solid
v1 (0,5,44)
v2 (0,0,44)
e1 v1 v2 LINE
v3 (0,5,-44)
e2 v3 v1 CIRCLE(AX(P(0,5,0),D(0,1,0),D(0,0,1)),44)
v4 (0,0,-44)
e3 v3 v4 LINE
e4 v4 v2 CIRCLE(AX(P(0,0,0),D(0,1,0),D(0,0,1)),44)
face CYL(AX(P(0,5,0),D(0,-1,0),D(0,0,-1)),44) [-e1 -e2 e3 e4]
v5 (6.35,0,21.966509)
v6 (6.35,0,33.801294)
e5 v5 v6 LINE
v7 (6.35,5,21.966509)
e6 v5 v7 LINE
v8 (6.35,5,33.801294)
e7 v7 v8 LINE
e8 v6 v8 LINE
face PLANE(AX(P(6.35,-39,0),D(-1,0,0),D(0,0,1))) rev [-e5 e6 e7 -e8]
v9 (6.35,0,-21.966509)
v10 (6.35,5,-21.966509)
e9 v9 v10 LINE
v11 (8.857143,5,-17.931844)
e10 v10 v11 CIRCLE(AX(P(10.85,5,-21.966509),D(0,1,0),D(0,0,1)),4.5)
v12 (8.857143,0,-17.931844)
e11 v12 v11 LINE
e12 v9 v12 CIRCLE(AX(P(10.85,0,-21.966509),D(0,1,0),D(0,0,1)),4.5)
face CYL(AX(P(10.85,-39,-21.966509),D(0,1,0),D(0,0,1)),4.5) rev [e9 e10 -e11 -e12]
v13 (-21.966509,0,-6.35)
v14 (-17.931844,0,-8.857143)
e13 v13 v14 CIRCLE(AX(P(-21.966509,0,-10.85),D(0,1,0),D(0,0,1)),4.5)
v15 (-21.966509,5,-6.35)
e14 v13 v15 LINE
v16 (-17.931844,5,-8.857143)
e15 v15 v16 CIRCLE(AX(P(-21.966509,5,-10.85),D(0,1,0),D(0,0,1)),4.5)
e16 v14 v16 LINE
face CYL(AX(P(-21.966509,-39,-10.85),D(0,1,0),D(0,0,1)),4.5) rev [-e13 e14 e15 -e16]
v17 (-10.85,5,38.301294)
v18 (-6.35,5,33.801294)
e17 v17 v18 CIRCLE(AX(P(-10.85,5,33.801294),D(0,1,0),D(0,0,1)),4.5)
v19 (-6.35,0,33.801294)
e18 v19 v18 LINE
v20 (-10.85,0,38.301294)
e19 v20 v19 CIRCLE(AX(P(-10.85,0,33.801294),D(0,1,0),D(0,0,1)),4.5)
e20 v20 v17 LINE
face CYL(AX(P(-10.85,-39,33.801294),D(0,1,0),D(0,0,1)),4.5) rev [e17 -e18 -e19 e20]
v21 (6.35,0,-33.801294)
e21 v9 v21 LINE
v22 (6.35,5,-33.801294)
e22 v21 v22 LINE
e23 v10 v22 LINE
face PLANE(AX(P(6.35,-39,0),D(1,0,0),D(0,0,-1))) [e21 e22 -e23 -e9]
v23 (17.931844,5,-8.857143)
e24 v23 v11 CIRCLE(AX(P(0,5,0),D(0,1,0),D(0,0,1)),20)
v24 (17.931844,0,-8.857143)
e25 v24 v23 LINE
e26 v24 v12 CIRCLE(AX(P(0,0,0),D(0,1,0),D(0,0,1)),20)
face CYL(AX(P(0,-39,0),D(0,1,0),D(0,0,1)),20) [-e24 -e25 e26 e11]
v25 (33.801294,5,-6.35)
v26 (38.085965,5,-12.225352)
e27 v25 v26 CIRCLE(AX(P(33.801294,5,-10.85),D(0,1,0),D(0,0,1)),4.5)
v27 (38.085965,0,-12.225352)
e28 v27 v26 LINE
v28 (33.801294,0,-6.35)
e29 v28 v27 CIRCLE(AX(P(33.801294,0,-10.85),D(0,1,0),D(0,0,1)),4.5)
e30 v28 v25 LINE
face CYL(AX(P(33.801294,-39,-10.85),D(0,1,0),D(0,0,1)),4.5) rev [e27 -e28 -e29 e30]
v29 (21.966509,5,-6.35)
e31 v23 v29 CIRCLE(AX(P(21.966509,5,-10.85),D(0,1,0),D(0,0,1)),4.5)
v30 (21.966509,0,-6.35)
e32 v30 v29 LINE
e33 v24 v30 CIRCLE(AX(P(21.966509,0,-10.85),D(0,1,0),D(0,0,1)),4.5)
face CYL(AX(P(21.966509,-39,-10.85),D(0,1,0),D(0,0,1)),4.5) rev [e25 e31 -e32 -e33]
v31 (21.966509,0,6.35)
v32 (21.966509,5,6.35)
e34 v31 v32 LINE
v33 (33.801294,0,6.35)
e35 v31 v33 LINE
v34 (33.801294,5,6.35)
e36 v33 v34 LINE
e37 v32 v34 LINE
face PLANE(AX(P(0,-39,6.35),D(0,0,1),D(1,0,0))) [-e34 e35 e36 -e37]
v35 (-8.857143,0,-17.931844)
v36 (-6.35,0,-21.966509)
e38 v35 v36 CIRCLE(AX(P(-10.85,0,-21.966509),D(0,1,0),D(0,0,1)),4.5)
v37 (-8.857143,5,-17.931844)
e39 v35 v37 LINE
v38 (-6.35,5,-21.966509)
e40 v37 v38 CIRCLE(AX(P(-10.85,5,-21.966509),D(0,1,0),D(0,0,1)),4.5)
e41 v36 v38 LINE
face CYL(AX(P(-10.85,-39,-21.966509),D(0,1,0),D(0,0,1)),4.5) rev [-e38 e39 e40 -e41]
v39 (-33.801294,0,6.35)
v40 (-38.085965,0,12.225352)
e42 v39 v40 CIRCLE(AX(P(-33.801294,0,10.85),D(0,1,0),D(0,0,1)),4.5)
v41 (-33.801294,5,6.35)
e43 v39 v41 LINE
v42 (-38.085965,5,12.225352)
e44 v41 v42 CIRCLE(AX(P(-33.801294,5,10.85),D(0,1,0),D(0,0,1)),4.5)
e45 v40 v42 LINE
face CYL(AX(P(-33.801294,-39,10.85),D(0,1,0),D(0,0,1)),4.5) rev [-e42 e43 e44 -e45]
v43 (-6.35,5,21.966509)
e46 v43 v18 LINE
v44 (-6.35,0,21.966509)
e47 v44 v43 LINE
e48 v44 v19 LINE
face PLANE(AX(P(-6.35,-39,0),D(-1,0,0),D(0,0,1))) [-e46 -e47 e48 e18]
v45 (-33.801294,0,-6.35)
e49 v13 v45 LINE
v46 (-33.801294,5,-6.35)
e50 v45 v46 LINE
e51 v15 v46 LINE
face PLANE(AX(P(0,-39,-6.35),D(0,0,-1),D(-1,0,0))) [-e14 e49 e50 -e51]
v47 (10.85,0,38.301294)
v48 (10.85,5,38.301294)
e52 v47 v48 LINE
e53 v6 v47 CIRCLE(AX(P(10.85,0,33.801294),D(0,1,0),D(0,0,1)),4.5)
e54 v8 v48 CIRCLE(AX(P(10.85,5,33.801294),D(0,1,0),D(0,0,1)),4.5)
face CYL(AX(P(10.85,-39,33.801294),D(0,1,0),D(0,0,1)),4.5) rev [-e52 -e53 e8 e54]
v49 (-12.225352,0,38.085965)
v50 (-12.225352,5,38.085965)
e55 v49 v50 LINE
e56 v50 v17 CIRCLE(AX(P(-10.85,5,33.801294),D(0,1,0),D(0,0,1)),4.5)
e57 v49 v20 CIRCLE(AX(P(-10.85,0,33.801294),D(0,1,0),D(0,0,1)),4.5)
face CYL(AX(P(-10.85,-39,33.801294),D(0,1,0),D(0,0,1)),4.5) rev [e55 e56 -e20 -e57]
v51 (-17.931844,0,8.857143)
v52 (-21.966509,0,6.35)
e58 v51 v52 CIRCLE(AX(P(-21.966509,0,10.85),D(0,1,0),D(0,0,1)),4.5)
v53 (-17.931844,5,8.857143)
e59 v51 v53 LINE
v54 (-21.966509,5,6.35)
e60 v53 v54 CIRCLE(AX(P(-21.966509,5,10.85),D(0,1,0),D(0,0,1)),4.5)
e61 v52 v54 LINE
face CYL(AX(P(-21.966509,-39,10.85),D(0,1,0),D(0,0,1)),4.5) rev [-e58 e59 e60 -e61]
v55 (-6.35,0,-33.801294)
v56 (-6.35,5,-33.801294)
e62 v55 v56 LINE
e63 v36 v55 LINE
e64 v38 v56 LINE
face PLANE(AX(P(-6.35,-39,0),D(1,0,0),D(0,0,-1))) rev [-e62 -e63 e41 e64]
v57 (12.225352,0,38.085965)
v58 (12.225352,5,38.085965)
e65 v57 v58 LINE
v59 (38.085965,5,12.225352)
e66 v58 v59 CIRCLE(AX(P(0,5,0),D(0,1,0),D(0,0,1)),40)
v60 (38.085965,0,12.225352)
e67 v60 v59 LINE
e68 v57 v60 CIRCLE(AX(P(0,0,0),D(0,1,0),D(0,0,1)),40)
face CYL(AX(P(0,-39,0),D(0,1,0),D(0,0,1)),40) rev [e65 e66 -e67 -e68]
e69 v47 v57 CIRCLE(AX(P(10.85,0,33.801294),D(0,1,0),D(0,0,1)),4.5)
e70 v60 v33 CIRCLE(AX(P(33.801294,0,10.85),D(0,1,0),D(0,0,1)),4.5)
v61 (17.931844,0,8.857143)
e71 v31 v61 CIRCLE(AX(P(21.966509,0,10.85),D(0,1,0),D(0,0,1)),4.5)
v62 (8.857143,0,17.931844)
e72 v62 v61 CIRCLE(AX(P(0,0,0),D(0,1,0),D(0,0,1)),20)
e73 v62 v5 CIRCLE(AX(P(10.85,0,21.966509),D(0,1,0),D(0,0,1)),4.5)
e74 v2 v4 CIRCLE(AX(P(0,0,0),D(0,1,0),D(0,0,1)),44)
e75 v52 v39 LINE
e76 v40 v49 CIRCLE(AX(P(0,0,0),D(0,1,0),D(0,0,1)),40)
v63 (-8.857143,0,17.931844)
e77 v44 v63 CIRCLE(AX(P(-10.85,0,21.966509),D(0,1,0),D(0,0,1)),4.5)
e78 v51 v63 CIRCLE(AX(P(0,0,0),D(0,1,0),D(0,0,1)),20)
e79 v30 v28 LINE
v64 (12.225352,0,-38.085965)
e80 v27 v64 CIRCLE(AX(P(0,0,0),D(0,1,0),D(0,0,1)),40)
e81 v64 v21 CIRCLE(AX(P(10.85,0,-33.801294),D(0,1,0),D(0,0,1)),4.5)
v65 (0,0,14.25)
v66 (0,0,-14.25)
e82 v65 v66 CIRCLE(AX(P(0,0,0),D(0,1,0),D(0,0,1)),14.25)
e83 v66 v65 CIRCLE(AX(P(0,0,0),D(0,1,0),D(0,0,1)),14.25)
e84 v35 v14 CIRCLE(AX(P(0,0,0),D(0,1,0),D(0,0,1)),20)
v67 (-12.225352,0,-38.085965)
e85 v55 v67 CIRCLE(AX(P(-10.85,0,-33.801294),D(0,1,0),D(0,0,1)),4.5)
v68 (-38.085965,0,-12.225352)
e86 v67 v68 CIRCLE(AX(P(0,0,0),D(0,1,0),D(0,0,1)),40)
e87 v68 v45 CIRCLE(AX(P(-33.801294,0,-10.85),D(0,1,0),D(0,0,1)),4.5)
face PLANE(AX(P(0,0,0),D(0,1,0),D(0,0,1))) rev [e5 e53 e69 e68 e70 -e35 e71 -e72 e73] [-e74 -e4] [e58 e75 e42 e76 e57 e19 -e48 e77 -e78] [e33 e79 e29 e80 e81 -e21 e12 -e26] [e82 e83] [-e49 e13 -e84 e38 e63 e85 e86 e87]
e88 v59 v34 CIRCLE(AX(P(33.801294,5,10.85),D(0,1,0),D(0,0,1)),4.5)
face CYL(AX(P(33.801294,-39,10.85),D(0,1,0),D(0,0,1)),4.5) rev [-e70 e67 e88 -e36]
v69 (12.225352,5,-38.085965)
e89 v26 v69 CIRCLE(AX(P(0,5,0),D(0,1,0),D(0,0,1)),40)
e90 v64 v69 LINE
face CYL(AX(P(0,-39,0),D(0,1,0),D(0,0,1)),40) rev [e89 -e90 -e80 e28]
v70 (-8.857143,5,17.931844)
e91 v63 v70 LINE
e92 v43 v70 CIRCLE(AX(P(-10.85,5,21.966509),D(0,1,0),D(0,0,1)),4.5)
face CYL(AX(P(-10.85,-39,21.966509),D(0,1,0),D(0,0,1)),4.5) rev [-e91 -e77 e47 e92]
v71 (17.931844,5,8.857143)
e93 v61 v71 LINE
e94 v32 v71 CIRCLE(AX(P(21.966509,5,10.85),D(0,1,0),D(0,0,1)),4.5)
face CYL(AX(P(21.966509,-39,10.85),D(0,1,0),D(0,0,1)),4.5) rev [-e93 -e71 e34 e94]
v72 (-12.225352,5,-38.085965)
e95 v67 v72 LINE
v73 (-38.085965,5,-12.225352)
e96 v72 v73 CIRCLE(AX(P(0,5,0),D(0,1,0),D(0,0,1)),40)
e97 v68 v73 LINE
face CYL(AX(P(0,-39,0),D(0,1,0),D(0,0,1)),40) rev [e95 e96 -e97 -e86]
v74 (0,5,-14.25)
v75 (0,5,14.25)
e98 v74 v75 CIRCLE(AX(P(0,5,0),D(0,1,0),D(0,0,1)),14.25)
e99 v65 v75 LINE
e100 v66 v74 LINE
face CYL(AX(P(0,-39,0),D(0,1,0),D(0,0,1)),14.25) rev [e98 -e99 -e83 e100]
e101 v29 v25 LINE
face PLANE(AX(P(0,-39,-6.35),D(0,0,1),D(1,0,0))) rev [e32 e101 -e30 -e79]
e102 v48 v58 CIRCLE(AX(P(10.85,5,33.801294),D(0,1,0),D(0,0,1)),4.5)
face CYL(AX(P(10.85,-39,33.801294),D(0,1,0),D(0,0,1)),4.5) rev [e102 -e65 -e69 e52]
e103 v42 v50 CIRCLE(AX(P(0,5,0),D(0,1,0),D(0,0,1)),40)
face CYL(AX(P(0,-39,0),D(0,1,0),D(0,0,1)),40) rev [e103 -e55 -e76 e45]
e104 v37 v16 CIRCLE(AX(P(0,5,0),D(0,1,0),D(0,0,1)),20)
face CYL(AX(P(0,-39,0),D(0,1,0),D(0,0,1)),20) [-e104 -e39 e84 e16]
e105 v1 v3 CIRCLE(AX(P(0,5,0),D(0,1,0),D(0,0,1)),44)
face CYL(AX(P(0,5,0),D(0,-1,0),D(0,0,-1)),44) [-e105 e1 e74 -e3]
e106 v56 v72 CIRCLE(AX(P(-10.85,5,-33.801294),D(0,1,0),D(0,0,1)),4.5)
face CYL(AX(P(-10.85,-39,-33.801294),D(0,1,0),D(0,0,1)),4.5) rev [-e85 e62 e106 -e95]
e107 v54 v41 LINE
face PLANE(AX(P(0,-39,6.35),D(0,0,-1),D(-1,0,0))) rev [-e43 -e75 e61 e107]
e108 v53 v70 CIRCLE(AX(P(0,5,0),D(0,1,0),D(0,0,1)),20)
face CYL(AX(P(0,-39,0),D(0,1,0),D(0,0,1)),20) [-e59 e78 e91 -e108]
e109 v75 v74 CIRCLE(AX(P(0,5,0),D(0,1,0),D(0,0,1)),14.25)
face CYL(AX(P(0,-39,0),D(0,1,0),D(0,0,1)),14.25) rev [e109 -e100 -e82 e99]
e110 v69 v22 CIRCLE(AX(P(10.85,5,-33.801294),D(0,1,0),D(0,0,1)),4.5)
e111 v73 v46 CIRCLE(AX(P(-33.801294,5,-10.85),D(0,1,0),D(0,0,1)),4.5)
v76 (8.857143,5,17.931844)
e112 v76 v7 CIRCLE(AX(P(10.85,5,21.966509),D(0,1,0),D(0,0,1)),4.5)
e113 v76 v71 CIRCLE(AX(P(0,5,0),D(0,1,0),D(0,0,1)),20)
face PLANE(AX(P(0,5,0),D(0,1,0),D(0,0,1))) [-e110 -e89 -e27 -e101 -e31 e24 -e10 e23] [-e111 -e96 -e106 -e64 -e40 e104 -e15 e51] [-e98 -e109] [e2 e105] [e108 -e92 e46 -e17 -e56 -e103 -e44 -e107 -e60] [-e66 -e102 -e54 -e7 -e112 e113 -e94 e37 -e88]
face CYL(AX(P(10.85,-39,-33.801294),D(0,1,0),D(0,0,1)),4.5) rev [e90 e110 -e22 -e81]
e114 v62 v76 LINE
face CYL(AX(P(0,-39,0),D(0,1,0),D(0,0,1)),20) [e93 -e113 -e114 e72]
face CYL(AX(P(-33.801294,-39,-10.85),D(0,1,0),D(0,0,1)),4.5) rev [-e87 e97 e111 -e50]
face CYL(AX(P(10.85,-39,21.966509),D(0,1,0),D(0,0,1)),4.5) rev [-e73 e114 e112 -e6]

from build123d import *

# Parameters (mm, degrees)
WEB_DISC_PROFILE_90_R                  = 44
WEB_DISC_90X5_DEPTH                    = 5
BORE_AND_SPOKE_WINDOWS_PROFILE_R       = 14.25
CENTRE_BORE_AND_4X_SPOKE_WINDOWS_DEPTH = 44


with BuildPart() as part:
    # Web Disc Profile Ø90 → Web Disc Ø90x5 (new body)
    with BuildSketch(Plane(origin=(0, 0, 0), x_dir=(1, 0, 0), z_dir=(0, 1, 0))):
        with Locations(Location((0, 0, 0), (0, 0, 270))):
            Circle(WEB_DISC_PROFILE_90_R)
    extrude(amount=WEB_DISC_90X5_DEPTH)

    # Bore and Spoke Windows Profile → Centre Bore and 4x Spoke Windows (cut)
    with BuildSketch(Plane(origin=(0, 5, 0), x_dir=(1, 0, 0), z_dir=(0, 1, 0))):
        with BuildLine():
            Line((-21.966508598, 6.35), (-33.801294354, 6.35))
            ThreePointArc((-33.801294354, 6.35), (-37.437163198, 8.198498964), (-38.085965469, 12.225352113))
            ThreePointArc((-38.085965469, 12.225352113), (-28.284271247, 28.284271247), (-12.225352113, 38.085965469))
            ThreePointArc((-12.225352113, 38.085965469), (-8.198498964, 37.437163198), (-6.35, 33.801294354))
            Line((-6.35, 33.801294354), (-6.35, 21.966508598))
            ThreePointArc((-6.35, 21.966508598), (-7.027837187, 19.591414615), (-8.857142857, 17.931843754))
            ThreePointArc((-8.857142857, 17.931843754), (-14.142135624, 14.142135624), (-17.931843754, 8.857142857))
            ThreePointArc((-17.931843754, 8.857142857), (-19.591414615, 7.027837187), (-21.966508598, 6.35))
        make_face()
        with BuildLine():
            Line((21.966508598, 6.35), (33.801294354, 6.35))
            ThreePointArc((33.801294354, 6.35), (37.437163198, 8.198498964), (38.085965469, 12.225352113))
            ThreePointArc((38.085965469, 12.225352113), (28.284271247, 28.284271247), (12.225352113, 38.085965469))
            ThreePointArc((12.225352113, 38.085965469), (8.198498964, 37.437163198), (6.35, 33.801294354))
            Line((6.35, 33.801294354), (6.35, 21.966508598))
            ThreePointArc((6.35, 21.966508598), (7.027837187, 19.591414615), (8.857142857, 17.931843754))
            ThreePointArc((8.857142857, 17.931843754), (14.142135624, 14.142135624), (17.931843754, 8.857142857))
            ThreePointArc((17.931843754, 8.857142857), (19.591414615, 7.027837187), (21.966508598, 6.35))
        make_face()
        with BuildLine():
            Line((21.966508598, -6.35), (33.801294354, -6.35))
            ThreePointArc((33.801294354, -6.35), (37.437163198, -8.198498964), (38.085965469, -12.225352113))
            ThreePointArc((38.085965469, -12.225352113), (28.284271247, -28.284271247), (12.225352113, -38.085965469))
            ThreePointArc((12.225352113, -38.085965469), (8.198498964, -37.437163198), (6.35, -33.801294354))
            Line((6.35, -33.801294354), (6.35, -21.966508598))
            ThreePointArc((6.35, -21.966508598), (7.027837187, -19.591414615), (8.857142857, -17.931843754))
            ThreePointArc((8.857142857, -17.931843754), (14.142135624, -14.142135624), (17.931843754, -8.857142857))
            ThreePointArc((17.931843754, -8.857142857), (19.591414615, -7.027837187), (21.966508598, -6.35))
        make_face()
        with BuildLine():
            Line((-6.35, -21.966508598), (-6.35, -33.801294354))
            ThreePointArc((-6.35, -33.801294354), (-8.198498964, -37.437163198), (-12.225352113, -38.085965469))
            ThreePointArc((-12.225352113, -38.085965469), (-28.284271247, -28.284271247), (-38.085965469, -12.225352113))
            ThreePointArc((-38.085965469, -12.225352113), (-37.437163198, -8.198498964), (-33.801294354, -6.35))
            Line((-33.801294354, -6.35), (-21.966508598, -6.35))
            ThreePointArc((-21.966508598, -6.35), (-19.591414615, -7.027837187), (-17.931843754, -8.857142857))
            ThreePointArc((-17.931843754, -8.857142857), (-14.142135624, -14.142135624), (-8.857142857, -17.931843754))
            ThreePointArc((-8.857142857, -17.931843754), (-7.027837187, -19.591414615), (-6.35, -21.966508598))
        make_face()
        with Locations(Location((0, 0, 0), (0, 0, 270))):
            Circle(BORE_AND_SPOKE_WINDOWS_PROFILE_R)
    extrude(amount=-CENTRE_BORE_AND_4X_SPOKE_WINDOWS_DEPTH, mode=Mode.SUBTRACT)


solid = part.part
